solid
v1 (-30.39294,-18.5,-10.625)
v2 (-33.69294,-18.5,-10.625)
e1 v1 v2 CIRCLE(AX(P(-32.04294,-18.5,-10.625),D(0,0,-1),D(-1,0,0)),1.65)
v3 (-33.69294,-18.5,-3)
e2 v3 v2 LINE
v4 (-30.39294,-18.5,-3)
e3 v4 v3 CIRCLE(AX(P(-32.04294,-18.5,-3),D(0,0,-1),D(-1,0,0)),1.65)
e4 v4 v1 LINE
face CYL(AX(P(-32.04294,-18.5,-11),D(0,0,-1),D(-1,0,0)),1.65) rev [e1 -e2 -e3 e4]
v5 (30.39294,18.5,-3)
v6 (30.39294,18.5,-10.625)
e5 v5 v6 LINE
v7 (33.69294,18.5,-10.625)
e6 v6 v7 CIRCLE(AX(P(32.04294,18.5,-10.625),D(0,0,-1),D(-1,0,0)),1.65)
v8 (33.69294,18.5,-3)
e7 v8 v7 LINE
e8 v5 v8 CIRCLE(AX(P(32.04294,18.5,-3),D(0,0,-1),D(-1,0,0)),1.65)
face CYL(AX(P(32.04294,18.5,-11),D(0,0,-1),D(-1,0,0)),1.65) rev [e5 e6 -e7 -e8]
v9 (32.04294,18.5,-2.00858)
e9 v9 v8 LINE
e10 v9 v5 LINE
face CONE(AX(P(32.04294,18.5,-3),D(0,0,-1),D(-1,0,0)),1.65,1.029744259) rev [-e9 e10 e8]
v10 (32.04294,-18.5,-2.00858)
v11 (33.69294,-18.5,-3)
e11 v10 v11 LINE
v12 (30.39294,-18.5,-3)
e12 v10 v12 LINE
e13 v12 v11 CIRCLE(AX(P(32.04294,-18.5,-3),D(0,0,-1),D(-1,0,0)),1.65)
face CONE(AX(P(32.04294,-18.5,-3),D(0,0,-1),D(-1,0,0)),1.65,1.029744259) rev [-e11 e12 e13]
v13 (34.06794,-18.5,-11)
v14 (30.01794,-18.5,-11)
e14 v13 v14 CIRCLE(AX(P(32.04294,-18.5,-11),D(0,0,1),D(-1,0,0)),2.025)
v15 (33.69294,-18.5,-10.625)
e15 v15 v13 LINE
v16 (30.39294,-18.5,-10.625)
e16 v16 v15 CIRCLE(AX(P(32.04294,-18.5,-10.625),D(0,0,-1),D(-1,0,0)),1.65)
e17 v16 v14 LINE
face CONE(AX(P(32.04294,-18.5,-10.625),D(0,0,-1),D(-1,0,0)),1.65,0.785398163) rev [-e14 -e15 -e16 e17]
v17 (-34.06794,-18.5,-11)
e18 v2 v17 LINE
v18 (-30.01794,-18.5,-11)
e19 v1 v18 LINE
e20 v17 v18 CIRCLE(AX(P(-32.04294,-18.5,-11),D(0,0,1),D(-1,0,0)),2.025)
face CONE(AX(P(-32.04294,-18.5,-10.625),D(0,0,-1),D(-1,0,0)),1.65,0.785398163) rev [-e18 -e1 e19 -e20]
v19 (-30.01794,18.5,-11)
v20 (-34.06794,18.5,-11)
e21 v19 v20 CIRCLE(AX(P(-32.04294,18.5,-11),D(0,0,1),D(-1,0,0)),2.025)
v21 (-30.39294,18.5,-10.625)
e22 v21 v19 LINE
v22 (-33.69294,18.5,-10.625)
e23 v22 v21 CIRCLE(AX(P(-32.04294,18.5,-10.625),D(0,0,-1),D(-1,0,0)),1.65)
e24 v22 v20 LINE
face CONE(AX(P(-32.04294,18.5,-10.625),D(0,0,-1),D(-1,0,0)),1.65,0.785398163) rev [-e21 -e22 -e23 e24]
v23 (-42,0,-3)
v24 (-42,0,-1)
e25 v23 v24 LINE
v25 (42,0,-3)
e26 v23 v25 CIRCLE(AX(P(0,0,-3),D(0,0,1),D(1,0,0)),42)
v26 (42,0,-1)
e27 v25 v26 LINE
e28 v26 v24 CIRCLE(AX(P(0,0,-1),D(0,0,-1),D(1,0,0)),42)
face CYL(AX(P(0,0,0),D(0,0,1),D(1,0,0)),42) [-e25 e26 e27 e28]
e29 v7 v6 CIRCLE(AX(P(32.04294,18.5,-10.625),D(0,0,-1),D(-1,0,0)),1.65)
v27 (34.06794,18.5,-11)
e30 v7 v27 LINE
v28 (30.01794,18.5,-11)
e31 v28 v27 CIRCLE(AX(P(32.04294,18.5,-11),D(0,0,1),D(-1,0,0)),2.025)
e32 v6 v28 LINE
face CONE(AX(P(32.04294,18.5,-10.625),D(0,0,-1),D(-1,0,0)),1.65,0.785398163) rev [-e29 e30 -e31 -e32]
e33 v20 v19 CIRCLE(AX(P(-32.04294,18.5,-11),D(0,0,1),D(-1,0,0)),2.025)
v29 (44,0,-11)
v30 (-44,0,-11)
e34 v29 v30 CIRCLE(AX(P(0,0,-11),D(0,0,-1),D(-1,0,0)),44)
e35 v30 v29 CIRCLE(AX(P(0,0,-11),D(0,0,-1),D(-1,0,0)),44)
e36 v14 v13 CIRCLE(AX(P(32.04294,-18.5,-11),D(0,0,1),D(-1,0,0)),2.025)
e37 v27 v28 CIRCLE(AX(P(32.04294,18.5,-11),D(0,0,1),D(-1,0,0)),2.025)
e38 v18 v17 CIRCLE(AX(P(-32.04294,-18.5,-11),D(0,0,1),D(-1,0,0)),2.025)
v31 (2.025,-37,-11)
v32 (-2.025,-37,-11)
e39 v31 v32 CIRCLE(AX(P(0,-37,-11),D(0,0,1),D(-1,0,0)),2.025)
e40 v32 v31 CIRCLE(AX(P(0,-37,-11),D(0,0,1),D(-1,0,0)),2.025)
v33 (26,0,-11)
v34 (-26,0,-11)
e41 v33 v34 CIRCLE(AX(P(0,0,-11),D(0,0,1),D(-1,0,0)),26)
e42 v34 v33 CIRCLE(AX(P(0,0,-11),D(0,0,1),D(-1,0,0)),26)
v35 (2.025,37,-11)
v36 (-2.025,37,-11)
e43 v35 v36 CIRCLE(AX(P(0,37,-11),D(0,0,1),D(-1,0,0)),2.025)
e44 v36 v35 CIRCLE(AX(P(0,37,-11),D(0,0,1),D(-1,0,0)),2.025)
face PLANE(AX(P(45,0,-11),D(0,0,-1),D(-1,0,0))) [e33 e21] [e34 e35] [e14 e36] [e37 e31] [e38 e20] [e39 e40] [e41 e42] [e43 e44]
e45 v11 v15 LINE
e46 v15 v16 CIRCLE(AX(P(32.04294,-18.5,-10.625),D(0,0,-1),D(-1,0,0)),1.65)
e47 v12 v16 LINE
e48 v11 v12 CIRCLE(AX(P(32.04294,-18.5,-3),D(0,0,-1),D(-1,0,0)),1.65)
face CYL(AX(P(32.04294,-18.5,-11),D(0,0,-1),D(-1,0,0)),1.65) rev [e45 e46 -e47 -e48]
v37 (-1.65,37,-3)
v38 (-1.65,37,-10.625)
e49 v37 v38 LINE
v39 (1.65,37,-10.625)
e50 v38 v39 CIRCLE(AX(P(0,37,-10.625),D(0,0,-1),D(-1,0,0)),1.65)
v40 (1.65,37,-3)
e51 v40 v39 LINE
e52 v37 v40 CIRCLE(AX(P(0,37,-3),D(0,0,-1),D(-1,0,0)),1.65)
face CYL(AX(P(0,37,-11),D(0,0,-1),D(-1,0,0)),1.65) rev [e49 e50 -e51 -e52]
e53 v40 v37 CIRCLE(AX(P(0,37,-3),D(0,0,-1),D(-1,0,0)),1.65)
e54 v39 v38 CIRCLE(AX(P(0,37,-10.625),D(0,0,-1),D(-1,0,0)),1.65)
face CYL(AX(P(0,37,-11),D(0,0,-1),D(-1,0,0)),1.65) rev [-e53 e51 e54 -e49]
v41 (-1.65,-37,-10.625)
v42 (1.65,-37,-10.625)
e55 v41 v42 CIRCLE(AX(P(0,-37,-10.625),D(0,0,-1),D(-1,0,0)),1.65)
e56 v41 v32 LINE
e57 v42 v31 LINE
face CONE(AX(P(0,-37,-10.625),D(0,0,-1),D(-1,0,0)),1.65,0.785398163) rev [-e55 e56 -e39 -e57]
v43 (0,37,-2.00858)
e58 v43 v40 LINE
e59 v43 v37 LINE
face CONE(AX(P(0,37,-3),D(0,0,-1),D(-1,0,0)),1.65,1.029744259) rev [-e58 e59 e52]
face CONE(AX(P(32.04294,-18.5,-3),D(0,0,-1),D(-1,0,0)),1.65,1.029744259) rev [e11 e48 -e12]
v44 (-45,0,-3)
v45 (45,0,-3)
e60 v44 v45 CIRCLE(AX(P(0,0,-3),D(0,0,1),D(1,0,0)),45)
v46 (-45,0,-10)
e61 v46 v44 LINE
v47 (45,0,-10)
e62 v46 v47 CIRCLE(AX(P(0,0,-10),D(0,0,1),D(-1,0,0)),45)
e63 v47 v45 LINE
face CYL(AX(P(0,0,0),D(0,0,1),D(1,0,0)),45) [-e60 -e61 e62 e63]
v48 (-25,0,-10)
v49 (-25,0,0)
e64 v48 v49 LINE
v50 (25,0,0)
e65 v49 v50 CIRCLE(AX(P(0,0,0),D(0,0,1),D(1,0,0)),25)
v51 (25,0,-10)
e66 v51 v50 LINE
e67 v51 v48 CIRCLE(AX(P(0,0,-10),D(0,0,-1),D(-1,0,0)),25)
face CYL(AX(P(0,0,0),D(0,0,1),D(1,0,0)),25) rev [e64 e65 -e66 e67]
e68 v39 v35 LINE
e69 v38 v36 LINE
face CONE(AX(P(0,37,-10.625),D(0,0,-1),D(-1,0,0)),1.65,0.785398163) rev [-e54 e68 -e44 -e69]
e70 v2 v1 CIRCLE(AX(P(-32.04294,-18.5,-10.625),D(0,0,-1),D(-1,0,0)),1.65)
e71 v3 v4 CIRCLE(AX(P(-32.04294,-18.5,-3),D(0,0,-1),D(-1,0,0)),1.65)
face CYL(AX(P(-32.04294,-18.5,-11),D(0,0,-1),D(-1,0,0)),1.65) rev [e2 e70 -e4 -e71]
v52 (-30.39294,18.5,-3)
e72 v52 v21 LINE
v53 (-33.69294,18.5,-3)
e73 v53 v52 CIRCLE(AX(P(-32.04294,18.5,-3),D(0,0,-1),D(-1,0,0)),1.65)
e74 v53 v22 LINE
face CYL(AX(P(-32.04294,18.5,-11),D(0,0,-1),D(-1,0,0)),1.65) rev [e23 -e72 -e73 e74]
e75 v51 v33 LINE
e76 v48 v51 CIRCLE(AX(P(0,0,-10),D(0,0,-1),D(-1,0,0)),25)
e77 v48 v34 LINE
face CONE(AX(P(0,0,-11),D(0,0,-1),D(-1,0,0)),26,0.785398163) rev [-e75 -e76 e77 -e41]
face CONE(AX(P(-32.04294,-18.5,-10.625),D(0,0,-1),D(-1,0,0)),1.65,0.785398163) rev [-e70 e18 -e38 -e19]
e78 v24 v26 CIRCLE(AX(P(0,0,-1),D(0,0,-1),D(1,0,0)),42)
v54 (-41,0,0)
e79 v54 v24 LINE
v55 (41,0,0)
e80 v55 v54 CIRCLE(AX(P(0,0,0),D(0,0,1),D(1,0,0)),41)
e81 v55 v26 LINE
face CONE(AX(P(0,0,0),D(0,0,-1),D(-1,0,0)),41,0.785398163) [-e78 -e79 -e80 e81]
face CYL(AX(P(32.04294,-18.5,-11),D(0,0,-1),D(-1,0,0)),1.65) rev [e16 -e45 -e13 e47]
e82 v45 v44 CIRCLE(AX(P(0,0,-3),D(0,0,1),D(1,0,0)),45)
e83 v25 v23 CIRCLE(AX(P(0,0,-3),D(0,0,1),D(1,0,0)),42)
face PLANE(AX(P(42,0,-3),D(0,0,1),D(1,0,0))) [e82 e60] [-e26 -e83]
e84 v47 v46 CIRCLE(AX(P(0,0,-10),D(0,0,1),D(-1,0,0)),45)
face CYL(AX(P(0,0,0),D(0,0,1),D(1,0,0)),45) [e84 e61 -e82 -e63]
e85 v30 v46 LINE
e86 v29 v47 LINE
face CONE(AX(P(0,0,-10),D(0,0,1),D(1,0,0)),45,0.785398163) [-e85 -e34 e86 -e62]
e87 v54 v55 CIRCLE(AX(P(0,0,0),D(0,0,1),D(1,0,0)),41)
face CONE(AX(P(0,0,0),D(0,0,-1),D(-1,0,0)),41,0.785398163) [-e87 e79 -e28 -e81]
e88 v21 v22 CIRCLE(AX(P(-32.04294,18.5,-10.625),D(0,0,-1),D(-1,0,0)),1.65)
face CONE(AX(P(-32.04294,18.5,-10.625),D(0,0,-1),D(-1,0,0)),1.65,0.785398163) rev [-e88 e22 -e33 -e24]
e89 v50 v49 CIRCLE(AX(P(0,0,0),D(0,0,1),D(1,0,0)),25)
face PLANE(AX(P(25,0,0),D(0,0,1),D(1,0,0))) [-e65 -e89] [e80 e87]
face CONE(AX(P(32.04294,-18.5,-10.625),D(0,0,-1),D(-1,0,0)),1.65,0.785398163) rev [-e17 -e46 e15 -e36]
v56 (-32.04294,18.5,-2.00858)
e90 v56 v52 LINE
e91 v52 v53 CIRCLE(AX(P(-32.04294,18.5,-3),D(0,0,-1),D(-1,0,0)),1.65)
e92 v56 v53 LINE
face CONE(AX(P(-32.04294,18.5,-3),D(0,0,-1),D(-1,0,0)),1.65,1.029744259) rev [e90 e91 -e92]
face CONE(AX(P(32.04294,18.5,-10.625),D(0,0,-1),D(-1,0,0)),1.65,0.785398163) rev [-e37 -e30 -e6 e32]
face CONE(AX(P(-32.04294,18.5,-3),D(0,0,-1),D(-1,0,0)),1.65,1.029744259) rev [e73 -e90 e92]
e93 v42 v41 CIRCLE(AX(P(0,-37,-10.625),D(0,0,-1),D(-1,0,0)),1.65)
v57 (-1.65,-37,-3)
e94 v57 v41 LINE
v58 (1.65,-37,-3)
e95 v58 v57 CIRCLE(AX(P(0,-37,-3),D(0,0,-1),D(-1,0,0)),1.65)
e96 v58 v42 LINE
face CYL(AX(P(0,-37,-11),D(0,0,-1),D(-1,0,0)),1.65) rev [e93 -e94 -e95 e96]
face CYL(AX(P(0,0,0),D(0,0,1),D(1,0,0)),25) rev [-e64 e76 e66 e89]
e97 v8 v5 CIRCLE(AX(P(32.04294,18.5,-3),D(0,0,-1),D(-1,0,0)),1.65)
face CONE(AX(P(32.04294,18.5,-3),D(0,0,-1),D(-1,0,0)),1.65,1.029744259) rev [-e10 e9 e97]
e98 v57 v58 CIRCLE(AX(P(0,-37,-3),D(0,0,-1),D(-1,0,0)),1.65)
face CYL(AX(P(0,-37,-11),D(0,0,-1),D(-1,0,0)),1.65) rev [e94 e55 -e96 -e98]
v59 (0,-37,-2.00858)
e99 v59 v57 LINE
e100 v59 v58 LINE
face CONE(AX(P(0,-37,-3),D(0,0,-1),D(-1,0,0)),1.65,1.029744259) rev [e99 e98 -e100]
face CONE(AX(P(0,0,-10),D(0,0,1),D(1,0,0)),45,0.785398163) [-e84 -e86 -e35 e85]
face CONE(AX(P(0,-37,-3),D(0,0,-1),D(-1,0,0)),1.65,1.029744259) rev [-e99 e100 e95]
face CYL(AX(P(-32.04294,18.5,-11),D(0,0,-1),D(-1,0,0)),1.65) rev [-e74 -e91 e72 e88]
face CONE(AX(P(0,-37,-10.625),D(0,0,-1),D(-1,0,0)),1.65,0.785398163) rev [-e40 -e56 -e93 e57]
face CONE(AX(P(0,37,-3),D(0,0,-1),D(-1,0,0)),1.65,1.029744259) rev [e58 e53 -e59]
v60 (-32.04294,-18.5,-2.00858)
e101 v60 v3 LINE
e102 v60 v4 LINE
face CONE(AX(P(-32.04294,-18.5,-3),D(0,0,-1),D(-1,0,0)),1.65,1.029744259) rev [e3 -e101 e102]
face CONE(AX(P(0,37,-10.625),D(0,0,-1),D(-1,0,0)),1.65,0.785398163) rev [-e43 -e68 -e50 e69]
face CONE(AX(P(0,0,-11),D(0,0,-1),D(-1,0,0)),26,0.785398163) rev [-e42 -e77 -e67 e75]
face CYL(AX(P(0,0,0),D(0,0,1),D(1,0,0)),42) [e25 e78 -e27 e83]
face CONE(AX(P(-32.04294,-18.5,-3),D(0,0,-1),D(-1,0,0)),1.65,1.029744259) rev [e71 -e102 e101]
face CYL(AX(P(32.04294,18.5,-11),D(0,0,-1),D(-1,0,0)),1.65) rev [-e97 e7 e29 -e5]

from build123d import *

# Parameters (mm, degrees)
SKETCH2_R             = 1.5
CUT_EXTRUDE1_DEPTH    = 3
M4_TAPPED_HOLE1_D     = 3.3
M4_TAPPED_HOLE1_DEPTH = 8
M4_TAPPED_HOLE1_TIP   = 0.991420021
CHAMFER1_SIZE         = 0.375
CHAMFER2_SIZE         = 1


with BuildPart() as part:
    # Sketch1 → Revolve1 (revolve)
    with BuildSketch(Plane(origin=(0, 0, 0), x_dir=(1, 0, 0), z_dir=(0, 1, 0))):
        Polygon((25, 0), (42, 0), (42, 3), (45, 3), (45, 11), (25, 11), align=None)
    revolve(axis=Axis((0, 0, 0), (0, 0, -1)))

    # Sketch2 → Cut-Extrude1 (cut)
    with BuildSketch(Plane(origin=(0, 0, -11), x_dir=(-1, 0, 0), z_dir=(0, 0, -1))):
        with Locations((0, -37)):
            Circle(SKETCH2_R)
        with Locations((-32.04293994, -18.5)):
            Circle(SKETCH2_R)
        with Locations((-32.04293994, 18.5)):
            Circle(SKETCH2_R)
        with Locations((0, 37)):
            Circle(SKETCH2_R)
        with Locations((32.04293994, 18.5)):
            Circle(SKETCH2_R)
        with Locations((32.04293994, -18.5)):
            Circle(SKETCH2_R)
    extrude(amount=-CUT_EXTRUDE1_DEPTH, mode=Mode.SUBTRACT)

    # M4 Tapped Hole1
    with Locations(Plane(origin=(0, 0, -11), x_dir=(-1, 0, 0), z_dir=(0, 0, -1))):
        with Locations((0, -37), (-32.04293994, -18.5), (-32.04293994, 18.5), (0, 37), (32.04293994, -18.5), (32.04293994, 18.5)):
            Hole(M4_TAPPED_HOLE1_D / 2, depth=M4_TAPPED_HOLE1_DEPTH)
            with Locations((0, 0, -(M4_TAPPED_HOLE1_DEPTH + M4_TAPPED_HOLE1_TIP / 2))):  # 118° drill point
                Cone(0, M4_TAPPED_HOLE1_D / 2, M4_TAPPED_HOLE1_TIP, mode=Mode.SUBTRACT)

    # Chamfer1
    chamfer1_edges = [part.edges().sort_by_distance(p)[0] for p in [
        (-33.69293994, 18.5, -11),
        (-33.69293994, -18.5, -11),
        (-1.65, 37, -11),
        (30.39293994, 18.5, -11),
        (30.39293994, -18.5, -11),
        (-1.65, -37, -11),
    ]]
    chamfer(chamfer1_edges, length=CHAMFER1_SIZE)

    # Chamfer2
    chamfer2_edges = [part.edges().sort_by_distance(p)[0] for p in [
        (-25, 0, -11),
        (-45, 0, -11),
        (-42, 0, 0),
    ]]
    chamfer(chamfer2_edges, length=CHAMFER2_SIZE)


solid = part.part
